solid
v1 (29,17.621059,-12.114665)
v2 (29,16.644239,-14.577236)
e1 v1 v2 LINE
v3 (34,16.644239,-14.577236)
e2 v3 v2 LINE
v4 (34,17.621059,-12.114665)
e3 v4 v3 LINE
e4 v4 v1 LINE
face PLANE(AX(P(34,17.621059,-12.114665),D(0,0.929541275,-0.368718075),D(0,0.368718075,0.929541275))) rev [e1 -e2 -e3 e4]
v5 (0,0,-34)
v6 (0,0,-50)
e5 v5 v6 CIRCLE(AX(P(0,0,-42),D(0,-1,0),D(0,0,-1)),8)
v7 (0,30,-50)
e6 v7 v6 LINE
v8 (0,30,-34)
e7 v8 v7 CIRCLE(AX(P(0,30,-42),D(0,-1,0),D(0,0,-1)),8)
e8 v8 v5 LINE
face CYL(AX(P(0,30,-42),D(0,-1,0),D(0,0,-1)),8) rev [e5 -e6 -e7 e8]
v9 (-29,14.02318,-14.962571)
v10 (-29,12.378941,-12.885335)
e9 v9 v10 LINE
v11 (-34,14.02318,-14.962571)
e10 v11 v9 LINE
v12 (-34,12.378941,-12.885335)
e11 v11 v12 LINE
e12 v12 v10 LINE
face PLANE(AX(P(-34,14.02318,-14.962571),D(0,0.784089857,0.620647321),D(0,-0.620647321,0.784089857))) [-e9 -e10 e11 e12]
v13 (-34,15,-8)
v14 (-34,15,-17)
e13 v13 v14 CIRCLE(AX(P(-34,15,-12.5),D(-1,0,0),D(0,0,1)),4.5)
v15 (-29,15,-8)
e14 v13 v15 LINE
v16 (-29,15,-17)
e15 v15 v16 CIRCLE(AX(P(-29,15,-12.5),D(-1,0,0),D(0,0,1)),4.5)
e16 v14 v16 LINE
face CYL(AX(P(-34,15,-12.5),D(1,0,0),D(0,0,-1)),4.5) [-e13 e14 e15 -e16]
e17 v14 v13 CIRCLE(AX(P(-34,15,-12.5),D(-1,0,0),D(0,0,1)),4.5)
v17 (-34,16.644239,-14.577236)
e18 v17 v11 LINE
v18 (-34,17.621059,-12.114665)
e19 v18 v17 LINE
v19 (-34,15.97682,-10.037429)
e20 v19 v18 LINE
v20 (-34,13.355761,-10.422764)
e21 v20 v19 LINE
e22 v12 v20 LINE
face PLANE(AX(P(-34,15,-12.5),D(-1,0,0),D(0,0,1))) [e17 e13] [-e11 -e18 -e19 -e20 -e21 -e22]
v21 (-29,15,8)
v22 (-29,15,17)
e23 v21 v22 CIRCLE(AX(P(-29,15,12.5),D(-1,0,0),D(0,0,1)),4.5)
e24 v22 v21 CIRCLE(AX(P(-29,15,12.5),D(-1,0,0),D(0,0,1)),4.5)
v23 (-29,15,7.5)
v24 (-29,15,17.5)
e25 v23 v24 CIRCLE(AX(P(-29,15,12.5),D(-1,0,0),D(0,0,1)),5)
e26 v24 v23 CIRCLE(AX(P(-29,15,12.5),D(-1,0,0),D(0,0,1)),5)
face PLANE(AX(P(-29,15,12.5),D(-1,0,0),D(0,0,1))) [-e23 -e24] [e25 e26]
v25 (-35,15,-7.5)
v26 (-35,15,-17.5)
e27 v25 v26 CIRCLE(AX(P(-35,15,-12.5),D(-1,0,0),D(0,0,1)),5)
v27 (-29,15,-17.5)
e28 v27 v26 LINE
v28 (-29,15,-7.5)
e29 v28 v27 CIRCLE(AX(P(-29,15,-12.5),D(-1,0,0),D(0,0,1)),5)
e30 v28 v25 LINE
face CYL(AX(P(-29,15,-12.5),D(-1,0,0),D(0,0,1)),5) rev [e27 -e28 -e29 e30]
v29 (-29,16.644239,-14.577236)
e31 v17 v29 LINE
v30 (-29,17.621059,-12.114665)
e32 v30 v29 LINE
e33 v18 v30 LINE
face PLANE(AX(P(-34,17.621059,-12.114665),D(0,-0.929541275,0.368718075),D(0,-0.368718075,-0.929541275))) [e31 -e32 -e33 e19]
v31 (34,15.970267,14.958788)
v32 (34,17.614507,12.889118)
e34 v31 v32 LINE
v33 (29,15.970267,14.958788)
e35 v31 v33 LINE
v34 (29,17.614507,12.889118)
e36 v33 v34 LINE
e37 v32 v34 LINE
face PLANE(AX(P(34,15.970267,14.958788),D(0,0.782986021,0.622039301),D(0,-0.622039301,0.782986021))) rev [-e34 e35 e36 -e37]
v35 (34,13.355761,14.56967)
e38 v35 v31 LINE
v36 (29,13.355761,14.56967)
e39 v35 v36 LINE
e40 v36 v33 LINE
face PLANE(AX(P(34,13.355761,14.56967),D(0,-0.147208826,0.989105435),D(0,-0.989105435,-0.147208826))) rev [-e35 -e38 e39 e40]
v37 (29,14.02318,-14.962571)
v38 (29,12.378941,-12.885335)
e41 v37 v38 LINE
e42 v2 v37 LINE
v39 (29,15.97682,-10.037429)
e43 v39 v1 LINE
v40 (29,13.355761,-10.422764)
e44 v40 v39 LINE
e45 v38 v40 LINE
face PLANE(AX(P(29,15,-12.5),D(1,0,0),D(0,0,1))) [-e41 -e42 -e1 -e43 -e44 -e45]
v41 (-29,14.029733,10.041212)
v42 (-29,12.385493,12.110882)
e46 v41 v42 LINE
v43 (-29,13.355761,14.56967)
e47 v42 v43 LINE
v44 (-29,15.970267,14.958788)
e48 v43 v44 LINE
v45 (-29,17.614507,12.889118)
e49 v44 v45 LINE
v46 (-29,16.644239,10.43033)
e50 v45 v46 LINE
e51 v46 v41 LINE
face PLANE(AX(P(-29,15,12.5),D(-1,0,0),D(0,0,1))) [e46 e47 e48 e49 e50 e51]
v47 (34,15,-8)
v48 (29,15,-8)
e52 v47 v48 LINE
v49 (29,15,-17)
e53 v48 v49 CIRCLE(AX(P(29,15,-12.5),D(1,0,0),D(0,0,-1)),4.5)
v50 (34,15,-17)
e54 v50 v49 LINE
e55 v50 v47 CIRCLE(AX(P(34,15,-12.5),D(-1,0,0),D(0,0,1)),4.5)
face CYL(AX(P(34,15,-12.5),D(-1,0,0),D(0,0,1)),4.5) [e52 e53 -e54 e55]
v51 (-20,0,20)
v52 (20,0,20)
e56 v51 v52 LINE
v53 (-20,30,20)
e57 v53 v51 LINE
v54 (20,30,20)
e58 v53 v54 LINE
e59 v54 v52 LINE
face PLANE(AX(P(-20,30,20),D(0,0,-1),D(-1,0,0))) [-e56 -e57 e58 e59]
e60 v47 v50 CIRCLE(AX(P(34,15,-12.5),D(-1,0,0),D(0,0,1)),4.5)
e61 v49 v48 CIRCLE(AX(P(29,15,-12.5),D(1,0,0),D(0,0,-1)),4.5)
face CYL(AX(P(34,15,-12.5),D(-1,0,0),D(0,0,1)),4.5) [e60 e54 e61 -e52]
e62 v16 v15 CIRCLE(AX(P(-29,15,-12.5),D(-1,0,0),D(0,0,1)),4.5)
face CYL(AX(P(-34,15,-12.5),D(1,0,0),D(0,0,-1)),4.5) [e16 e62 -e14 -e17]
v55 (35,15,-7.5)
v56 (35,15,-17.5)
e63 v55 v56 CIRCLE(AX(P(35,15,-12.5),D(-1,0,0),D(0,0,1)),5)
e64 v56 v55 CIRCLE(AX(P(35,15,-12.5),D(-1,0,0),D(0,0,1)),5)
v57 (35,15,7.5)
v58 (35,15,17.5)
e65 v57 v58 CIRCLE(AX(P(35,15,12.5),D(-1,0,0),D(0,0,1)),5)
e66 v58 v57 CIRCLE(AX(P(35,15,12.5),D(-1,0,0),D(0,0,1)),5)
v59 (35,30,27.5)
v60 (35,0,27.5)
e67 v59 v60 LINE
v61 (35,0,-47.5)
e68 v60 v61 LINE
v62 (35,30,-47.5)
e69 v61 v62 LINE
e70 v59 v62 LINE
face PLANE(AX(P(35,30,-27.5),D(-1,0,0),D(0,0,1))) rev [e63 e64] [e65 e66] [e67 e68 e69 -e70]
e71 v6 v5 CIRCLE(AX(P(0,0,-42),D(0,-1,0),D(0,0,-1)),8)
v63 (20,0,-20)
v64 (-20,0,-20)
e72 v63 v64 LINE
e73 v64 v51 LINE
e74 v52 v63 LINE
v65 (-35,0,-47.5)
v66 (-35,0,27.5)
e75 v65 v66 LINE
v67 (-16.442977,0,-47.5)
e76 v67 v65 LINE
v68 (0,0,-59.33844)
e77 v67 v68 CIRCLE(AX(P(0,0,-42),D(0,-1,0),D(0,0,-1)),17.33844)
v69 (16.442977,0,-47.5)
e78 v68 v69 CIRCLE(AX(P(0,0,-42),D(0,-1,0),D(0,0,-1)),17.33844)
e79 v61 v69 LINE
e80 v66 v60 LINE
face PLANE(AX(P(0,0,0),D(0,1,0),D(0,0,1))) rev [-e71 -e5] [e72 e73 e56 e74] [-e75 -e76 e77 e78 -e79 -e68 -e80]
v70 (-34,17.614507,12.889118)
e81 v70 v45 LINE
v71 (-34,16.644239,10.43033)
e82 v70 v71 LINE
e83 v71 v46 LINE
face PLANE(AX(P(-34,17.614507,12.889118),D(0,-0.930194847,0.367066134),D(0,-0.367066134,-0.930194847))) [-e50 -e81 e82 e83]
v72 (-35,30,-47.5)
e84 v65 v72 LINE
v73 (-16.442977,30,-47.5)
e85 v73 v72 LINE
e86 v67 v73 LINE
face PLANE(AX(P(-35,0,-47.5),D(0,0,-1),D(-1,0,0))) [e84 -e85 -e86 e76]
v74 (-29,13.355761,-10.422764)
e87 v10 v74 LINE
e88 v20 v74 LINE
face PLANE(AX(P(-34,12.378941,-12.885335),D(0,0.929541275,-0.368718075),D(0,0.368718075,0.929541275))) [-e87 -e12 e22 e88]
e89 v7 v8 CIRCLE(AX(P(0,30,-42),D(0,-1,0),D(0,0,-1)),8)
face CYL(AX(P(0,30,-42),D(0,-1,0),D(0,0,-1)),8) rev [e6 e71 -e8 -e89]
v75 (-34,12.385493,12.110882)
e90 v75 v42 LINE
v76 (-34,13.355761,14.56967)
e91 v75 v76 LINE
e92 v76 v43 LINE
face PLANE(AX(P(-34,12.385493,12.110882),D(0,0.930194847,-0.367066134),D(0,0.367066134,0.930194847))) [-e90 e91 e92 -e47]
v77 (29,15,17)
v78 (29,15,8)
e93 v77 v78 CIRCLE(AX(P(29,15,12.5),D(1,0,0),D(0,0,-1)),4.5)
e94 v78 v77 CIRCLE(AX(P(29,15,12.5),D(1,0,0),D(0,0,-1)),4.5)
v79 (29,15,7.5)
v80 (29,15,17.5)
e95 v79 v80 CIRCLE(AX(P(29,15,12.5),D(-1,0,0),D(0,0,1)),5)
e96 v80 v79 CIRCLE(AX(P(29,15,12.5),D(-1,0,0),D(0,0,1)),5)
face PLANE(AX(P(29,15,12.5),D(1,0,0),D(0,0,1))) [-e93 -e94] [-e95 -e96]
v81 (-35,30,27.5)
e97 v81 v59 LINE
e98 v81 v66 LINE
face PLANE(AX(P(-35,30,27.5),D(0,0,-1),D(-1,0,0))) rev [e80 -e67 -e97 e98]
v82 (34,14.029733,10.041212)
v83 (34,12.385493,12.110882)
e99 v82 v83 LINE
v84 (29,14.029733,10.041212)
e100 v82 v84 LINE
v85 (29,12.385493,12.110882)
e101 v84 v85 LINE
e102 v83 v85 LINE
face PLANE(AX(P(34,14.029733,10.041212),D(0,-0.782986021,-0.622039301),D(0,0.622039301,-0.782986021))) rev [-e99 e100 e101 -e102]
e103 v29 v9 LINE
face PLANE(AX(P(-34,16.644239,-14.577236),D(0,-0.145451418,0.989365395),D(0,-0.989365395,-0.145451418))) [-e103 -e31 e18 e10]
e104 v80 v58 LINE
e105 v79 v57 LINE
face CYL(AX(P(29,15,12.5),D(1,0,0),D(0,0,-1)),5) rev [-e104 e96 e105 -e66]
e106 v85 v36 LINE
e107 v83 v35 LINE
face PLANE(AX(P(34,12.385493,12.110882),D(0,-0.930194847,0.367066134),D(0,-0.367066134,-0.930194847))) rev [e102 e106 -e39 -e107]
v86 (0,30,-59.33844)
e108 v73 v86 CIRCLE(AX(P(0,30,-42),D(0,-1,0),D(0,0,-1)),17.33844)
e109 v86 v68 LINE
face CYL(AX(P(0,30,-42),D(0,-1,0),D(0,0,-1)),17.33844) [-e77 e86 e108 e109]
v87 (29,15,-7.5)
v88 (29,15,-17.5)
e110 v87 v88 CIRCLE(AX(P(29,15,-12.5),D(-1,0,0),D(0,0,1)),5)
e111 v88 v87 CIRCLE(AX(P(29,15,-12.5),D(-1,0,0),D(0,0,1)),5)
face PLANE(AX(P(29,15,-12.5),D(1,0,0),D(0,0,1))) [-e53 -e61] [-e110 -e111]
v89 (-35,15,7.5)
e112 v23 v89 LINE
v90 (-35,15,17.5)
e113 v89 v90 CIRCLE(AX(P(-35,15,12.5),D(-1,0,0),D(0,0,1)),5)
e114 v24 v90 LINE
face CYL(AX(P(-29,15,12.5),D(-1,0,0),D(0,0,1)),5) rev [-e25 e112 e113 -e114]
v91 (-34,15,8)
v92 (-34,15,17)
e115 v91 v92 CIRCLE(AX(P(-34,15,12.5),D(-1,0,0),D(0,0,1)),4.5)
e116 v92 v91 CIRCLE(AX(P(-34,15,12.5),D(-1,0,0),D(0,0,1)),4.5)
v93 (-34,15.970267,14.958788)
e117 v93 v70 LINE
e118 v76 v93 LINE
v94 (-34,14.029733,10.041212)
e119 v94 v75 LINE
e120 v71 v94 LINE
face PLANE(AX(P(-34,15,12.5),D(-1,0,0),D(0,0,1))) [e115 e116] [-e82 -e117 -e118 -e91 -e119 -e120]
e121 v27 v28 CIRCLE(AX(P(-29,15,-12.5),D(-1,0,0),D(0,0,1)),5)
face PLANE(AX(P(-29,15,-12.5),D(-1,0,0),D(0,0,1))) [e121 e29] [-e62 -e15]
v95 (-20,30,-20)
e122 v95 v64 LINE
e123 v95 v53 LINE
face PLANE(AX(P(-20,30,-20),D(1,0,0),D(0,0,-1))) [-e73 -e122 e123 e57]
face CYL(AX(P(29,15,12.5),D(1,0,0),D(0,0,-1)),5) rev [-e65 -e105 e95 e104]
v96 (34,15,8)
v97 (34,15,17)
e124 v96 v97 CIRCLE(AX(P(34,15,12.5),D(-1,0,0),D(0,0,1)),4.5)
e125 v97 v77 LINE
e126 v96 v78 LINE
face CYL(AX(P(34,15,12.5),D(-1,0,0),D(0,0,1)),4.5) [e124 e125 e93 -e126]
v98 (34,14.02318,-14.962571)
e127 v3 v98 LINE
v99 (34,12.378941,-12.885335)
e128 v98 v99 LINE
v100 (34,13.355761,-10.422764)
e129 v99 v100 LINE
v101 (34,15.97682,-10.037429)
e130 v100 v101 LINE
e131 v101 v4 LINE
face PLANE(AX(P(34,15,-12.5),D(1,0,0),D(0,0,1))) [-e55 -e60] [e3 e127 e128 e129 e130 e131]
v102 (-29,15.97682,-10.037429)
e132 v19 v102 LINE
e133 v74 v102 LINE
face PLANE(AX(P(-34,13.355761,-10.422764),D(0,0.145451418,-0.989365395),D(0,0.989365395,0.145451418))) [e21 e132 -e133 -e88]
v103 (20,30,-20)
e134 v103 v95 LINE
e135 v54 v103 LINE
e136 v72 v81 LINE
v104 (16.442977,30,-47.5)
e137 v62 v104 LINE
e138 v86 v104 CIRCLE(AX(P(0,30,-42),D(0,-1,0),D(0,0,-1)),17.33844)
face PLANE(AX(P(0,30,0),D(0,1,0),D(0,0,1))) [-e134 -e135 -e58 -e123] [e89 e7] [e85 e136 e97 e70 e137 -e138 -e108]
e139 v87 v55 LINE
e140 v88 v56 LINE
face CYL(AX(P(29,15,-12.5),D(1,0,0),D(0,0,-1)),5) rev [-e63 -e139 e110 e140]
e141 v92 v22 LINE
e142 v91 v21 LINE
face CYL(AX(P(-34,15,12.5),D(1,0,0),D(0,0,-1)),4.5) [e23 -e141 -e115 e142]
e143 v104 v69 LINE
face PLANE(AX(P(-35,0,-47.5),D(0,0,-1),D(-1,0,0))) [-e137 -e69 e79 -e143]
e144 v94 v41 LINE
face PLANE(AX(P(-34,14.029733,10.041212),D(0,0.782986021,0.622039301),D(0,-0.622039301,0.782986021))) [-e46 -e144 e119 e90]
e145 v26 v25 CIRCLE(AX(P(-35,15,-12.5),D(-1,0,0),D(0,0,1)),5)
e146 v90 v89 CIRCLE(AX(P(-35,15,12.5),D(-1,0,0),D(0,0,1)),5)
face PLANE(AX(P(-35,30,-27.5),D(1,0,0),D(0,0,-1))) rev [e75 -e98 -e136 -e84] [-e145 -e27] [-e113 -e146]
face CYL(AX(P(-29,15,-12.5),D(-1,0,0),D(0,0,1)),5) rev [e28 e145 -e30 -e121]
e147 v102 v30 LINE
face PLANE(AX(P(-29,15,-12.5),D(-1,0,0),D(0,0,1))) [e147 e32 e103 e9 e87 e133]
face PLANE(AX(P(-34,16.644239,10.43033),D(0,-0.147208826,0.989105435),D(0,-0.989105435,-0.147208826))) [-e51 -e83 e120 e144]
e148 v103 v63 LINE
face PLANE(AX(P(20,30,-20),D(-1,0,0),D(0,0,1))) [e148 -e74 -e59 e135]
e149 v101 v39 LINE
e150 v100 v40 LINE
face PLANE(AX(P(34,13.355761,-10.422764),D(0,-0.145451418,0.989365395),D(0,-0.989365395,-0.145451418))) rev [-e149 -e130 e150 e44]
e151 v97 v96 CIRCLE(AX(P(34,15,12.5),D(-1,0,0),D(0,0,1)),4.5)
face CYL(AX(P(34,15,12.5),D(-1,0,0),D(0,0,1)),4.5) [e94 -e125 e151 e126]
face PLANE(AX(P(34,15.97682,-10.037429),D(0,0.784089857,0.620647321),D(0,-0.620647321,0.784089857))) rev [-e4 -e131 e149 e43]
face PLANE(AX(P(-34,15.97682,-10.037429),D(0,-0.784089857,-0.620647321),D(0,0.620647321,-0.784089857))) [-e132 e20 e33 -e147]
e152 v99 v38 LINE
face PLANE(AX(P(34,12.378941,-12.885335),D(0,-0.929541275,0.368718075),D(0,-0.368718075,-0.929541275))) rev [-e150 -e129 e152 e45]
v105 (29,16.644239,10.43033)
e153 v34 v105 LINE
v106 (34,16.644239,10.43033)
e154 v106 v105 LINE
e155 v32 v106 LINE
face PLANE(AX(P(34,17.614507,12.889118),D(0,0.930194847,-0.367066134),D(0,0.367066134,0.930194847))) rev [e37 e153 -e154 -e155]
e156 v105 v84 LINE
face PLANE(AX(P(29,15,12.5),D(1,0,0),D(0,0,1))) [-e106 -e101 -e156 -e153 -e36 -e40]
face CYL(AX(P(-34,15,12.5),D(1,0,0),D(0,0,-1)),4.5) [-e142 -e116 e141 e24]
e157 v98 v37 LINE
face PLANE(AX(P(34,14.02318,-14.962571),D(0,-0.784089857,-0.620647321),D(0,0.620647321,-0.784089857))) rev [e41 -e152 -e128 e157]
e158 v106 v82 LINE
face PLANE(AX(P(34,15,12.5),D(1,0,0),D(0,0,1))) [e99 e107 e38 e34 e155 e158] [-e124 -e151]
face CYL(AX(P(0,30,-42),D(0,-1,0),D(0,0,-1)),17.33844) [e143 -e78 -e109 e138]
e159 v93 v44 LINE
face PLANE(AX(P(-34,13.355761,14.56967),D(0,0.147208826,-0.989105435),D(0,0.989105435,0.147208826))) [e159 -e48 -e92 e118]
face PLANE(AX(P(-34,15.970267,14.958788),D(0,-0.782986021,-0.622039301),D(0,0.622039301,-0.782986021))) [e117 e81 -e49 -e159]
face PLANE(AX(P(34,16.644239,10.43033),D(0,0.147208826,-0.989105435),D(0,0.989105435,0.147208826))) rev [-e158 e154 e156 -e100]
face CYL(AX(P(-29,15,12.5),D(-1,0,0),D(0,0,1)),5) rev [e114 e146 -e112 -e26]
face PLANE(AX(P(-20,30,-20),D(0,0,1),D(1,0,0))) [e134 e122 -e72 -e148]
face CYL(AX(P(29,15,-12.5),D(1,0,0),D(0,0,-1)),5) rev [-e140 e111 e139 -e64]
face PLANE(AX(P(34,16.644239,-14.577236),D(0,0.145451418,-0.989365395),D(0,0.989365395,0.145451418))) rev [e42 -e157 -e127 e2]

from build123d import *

# Parameters (mm, degrees)
SKETCH1_W           = 70
SKETCH1_H           = 55
SKETCH1_W_2         = 40
SKETCH1_H_2         = 40
BOSS_EXTRUDE1_DEPTH = 30
SKETCH2_W           = 70
SKETCH2_H           = 20
BOSS_EXTRUDE2_DEPTH = 30
SKETCH3_R           = 8
CUT_EXTRUDE1_DEPTH  = 30
SKETCH4_R           = 17.338439929
SKETCH4_R_2         = 8
BOSS_EXTRUDE3_DEPTH = 30
SKETCH5_R           = 5
CUT_EXTRUDE2_DEPTH  = 6
SKETCH6_R           = 4.5
BOSS_EXTRUDE4_DEPTH = 5


with BuildPart() as part:
    # Sketch1 → Boss-Extrude1 (new body)
    with BuildSketch(Plane(origin=(0, 0, 0), x_dir=(1, 0, 0), z_dir=(0, 1, 0))):
        Rectangle(SKETCH1_W, SKETCH1_H)
        Rectangle(SKETCH1_W_2, SKETCH1_H_2, mode=Mode.SUBTRACT)
    extrude(amount=BOSS_EXTRUDE1_DEPTH)

    # Sketch2 → Boss-Extrude2 (add)
    with BuildSketch(Plane(origin=(0, 30, 0), x_dir=(1, 0, 0), z_dir=(0, 1, 0))):
        with Locations((0, 37.5)):
            Rectangle(SKETCH2_W, SKETCH2_H)
    extrude(amount=-BOSS_EXTRUDE2_DEPTH)

    # Sketch3 → Cut-Extrude1 (cut)
    with BuildSketch(Plane.XZ):
        with Locations((0, -42)):
            Circle(SKETCH3_R)
    extrude(amount=-CUT_EXTRUDE1_DEPTH, mode=Mode.SUBTRACT)

    # Sketch4 → Boss-Extrude3 (add)
    with BuildSketch(Plane.XZ):
        with Locations((0, -42)):
            Circle(SKETCH4_R)
        with Locations(Location((0, -42, 0), (0, 0, 270))):
            Circle(SKETCH4_R_2, mode=Mode.SUBTRACT)
    extrude(amount=-BOSS_EXTRUDE3_DEPTH)

    # Sketch5 → Cut-Extrude2 (cut)
    with BuildSketch(Plane.ZY.offset(35)):
        with Locations((12.5, 15)):
            Circle(SKETCH5_R)
        with Locations((-12.5, 15)):
            Circle(SKETCH5_R)
    cut_extrude2 = extrude(amount=-CUT_EXTRUDE2_DEPTH, mode=Mode.SUBTRACT)

    # Sketch6 → Boss-Extrude4 (add)
    # profile 1 of 2: a face of its own
    with BuildSketch(Plane.ZY.offset(29)):
        with Locations((-12.5, 15)):
            Circle(SKETCH6_R)
        Polygon((-10.422763648, 13.355760931), (-10.03742902, 15.976819916), (-12.114665372, 17.621058985), (-14.577236352, 16.644239069), (-14.96257098, 14.023180084), (-12.885334628, 12.378941015), align=None, mode=Mode.SUBTRACT)
    # profile 2 of 2: a face of its own
    with BuildSketch(Plane.ZY.offset(29)):
        with Locations((12.5, 15)):
            Circle(SKETCH6_R)
        Polygon((14.569670203, 13.355760931), (14.958787905, 15.970267439), (12.889117702, 17.614506508), (10.430329797, 16.644239069), (10.041212095, 14.029732561), (12.110882298, 12.385493492), align=None, mode=Mode.SUBTRACT)
    boss_extrude4 = extrude(amount=BOSS_EXTRUDE4_DEPTH)

    # Mirror1: Cut-Extrude2, Boss-Extrude4 across plane
    add(cut_extrude2.mirror(Plane(origin=(0, 0, 0), x_dir=(0, 0, 1), z_dir=(1, 0, 0))), mode=Mode.SUBTRACT)
    add(boss_extrude4.mirror(Plane(origin=(0, 0, 0), x_dir=(0, 0, 1), z_dir=(1, 0, 0))))


solid = part.part
